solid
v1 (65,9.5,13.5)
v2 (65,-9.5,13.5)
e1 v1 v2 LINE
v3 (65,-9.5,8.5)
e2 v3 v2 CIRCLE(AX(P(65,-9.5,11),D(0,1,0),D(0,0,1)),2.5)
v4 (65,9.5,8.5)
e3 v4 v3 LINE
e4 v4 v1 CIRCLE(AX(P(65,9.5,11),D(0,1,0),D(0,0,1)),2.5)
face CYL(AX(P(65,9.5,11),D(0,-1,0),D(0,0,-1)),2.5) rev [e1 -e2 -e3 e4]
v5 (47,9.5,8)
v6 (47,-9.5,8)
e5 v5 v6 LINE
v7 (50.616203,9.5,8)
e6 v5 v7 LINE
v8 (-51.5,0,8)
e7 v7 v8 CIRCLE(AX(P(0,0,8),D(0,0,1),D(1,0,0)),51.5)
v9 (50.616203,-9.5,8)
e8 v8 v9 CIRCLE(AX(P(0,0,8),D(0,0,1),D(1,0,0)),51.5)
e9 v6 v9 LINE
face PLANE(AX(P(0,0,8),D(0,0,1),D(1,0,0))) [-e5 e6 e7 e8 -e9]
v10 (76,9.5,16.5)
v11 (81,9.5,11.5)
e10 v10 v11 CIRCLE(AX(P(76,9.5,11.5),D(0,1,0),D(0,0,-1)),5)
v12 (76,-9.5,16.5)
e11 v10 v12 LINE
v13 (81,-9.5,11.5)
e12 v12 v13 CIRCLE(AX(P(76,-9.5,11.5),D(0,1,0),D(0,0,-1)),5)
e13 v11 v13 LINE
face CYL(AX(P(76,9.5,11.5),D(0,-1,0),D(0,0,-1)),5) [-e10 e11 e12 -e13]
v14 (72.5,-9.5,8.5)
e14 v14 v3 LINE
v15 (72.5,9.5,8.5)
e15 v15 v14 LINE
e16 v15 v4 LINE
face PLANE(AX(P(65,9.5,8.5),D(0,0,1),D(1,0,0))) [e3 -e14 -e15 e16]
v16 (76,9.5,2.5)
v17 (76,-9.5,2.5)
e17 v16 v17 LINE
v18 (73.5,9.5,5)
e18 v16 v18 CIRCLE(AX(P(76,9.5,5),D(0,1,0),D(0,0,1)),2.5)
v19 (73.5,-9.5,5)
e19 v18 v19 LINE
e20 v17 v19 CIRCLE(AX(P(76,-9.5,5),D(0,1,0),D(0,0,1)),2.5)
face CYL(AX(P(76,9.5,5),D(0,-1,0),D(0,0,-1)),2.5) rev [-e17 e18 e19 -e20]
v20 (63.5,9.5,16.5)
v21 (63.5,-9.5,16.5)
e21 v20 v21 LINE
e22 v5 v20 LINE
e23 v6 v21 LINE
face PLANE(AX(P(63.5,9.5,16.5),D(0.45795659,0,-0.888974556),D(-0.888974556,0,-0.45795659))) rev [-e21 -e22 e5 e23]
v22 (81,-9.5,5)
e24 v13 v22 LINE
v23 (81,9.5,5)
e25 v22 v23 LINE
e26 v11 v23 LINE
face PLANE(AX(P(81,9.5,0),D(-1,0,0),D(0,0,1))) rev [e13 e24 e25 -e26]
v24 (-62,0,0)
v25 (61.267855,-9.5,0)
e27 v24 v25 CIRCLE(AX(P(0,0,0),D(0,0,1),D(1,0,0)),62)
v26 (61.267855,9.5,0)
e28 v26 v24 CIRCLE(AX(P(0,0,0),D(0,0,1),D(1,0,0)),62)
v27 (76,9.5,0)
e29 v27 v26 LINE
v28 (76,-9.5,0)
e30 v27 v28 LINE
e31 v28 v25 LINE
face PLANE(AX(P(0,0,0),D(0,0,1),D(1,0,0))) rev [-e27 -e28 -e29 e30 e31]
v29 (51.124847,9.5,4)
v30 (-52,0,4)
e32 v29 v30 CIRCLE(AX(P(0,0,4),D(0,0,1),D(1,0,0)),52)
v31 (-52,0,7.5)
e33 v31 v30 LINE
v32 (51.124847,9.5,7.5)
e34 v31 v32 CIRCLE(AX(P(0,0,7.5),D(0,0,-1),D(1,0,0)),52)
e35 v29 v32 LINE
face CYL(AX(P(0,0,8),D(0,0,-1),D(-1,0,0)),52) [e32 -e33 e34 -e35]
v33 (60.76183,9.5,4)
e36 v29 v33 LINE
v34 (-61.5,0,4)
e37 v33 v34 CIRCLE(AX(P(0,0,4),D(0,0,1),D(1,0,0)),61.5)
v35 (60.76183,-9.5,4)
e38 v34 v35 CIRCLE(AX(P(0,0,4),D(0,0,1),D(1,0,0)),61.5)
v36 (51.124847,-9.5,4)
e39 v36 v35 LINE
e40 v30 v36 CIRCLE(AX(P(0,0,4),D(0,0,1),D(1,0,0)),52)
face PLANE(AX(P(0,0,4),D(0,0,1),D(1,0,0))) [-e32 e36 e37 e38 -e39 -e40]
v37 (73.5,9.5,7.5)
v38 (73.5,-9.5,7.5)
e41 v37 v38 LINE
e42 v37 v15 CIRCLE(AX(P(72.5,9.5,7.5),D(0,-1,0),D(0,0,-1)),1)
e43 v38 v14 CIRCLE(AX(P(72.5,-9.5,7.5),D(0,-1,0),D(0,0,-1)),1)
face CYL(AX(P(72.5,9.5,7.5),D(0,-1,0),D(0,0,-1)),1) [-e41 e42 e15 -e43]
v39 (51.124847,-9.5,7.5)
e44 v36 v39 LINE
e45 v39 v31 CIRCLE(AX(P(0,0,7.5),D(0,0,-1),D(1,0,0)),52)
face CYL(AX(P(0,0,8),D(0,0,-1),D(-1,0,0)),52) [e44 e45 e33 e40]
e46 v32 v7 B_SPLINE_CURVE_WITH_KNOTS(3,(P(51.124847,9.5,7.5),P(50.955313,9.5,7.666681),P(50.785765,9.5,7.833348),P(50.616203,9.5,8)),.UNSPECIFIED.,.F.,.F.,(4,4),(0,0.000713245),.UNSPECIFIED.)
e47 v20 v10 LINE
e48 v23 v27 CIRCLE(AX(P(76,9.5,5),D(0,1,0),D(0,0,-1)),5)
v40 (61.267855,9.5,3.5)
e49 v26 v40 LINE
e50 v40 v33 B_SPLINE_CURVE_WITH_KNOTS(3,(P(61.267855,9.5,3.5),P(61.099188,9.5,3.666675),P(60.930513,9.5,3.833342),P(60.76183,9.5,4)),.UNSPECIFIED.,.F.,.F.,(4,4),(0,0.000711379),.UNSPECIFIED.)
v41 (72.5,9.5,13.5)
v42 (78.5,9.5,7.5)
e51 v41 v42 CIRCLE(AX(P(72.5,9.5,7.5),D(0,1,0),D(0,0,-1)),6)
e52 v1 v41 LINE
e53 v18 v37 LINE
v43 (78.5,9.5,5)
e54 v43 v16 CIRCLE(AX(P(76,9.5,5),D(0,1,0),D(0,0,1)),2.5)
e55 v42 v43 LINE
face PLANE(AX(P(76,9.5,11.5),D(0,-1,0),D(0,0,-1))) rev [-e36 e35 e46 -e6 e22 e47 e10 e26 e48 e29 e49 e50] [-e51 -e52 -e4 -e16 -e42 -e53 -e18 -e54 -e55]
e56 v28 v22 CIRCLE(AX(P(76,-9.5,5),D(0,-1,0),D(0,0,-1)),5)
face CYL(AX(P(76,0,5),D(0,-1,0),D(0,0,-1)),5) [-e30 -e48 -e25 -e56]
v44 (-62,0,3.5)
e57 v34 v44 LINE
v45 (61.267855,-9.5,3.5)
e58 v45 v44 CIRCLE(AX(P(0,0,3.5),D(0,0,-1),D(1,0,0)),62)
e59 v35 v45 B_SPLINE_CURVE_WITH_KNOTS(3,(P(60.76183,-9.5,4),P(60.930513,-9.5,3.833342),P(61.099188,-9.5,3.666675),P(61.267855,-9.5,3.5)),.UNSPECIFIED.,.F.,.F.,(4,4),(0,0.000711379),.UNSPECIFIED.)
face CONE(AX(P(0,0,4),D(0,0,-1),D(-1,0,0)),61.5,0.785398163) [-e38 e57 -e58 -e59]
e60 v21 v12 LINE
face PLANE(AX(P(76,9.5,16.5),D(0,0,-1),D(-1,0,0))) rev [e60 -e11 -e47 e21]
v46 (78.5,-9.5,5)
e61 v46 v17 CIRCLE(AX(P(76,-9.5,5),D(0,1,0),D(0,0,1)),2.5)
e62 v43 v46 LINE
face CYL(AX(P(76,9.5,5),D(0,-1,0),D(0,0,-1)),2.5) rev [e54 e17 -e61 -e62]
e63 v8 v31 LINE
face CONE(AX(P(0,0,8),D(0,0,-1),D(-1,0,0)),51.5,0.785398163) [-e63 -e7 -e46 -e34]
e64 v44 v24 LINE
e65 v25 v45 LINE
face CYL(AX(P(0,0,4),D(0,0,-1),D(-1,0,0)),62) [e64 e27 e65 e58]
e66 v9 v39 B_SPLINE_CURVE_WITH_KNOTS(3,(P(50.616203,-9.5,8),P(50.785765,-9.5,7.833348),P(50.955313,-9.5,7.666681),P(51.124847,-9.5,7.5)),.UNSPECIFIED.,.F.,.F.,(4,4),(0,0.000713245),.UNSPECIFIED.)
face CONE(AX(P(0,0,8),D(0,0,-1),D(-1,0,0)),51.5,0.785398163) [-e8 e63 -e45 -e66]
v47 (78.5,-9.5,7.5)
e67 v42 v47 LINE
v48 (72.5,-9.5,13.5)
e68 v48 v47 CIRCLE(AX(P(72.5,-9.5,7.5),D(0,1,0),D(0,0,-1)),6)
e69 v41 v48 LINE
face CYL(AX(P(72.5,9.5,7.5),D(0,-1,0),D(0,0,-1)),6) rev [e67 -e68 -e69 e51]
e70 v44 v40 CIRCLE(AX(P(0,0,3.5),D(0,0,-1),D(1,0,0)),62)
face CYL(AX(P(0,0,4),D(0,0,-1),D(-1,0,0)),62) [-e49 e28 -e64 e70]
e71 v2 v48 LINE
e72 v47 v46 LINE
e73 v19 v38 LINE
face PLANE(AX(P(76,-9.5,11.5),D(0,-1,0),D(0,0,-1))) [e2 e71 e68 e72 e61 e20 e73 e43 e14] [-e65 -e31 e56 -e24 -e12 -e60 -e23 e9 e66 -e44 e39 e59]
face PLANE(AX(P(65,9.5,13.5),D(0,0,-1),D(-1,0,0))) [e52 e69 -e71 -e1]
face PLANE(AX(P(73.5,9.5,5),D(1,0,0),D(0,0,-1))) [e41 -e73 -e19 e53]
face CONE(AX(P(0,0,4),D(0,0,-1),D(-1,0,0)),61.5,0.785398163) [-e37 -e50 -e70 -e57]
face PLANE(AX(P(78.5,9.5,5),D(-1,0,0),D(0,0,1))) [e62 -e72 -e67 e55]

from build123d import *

# Parameters (mm, degrees)
SKETCH_1_R      = 62
EXTRUDE_1_DEPTH = 4
SKETCH_2_R      = 52
EXTRUDE_2_DEPTH = 4
EXTRUDE_3_DEPTH = 9.5
FILLET_1_R      = 5
CHAMFER_1_SIZE  = 0.5


with BuildPart() as part:
    # 草图1 → 凸台-拉伸1 (new body)
    with BuildSketch(Plane.XY):
        Circle(SKETCH_1_R)
    extrude(amount=EXTRUDE_1_DEPTH)

    # 草图2 → 凸台-拉伸2 (add)
    with BuildSketch(Plane.XY.offset(4)):
        Circle(SKETCH_2_R)
    extrude(amount=EXTRUDE_2_DEPTH)

    # 草图3 → 凸台-拉伸3 (add, symmetric)
    with BuildSketch(Plane(origin=(0, 0, 0), x_dir=(1, 0, 0), z_dir=(0, 1, 0))):
        with BuildLine():
            Line((81, 0), (81, -11.5))
            ThreePointArc((81, -11.5), (79.535533906, -15.035533906), (76, -16.5))
            Line((76, -16.5), (63.5, -16.5))
            Line((63.5, -16.5), (47, -8))
            Line((47, -8), (47, 0))
            Line((47, 0), (81, 0))
        make_face()
        with BuildLine():
            Line((73.5, -5), (73.5, -7.5))
            ThreePointArc((73.5, -7.5), (73.207106781, -8.207106781), (72.5, -8.5))
            Line((72.5, -8.5), (65, -8.5))
            ThreePointArc((65, -8.5), (62.5, -11), (65, -13.5))
            Line((65, -13.5), (72.5, -13.5))
            ThreePointArc((72.5, -13.5), (76.742640687, -11.742640687), (78.5, -7.5))
            Line((78.5, -7.5), (78.5, -5))
            ThreePointArc((78.5, -5), (76, -2.5), (73.5, -5))
        make_face(mode=Mode.SUBTRACT)
    extrude(amount=EXTRUDE_3_DEPTH, both=True)

    # 圆角1
    fillet_1_edges = [part.edges().sort_by_distance(p)[0] for p in [
        (81, 0, 0),
    ]]
    fillet(fillet_1_edges, radius=FILLET_1_R)

    # 倒角1
    chamfer_1_edges = [part.edges().sort_by_distance(p)[0] for p in [
        (-62, 0, 4),
        (-52, 0, 8),
    ]]
    chamfer(chamfer_1_edges, length=CHAMFER_1_SIZE)


solid = part.part
